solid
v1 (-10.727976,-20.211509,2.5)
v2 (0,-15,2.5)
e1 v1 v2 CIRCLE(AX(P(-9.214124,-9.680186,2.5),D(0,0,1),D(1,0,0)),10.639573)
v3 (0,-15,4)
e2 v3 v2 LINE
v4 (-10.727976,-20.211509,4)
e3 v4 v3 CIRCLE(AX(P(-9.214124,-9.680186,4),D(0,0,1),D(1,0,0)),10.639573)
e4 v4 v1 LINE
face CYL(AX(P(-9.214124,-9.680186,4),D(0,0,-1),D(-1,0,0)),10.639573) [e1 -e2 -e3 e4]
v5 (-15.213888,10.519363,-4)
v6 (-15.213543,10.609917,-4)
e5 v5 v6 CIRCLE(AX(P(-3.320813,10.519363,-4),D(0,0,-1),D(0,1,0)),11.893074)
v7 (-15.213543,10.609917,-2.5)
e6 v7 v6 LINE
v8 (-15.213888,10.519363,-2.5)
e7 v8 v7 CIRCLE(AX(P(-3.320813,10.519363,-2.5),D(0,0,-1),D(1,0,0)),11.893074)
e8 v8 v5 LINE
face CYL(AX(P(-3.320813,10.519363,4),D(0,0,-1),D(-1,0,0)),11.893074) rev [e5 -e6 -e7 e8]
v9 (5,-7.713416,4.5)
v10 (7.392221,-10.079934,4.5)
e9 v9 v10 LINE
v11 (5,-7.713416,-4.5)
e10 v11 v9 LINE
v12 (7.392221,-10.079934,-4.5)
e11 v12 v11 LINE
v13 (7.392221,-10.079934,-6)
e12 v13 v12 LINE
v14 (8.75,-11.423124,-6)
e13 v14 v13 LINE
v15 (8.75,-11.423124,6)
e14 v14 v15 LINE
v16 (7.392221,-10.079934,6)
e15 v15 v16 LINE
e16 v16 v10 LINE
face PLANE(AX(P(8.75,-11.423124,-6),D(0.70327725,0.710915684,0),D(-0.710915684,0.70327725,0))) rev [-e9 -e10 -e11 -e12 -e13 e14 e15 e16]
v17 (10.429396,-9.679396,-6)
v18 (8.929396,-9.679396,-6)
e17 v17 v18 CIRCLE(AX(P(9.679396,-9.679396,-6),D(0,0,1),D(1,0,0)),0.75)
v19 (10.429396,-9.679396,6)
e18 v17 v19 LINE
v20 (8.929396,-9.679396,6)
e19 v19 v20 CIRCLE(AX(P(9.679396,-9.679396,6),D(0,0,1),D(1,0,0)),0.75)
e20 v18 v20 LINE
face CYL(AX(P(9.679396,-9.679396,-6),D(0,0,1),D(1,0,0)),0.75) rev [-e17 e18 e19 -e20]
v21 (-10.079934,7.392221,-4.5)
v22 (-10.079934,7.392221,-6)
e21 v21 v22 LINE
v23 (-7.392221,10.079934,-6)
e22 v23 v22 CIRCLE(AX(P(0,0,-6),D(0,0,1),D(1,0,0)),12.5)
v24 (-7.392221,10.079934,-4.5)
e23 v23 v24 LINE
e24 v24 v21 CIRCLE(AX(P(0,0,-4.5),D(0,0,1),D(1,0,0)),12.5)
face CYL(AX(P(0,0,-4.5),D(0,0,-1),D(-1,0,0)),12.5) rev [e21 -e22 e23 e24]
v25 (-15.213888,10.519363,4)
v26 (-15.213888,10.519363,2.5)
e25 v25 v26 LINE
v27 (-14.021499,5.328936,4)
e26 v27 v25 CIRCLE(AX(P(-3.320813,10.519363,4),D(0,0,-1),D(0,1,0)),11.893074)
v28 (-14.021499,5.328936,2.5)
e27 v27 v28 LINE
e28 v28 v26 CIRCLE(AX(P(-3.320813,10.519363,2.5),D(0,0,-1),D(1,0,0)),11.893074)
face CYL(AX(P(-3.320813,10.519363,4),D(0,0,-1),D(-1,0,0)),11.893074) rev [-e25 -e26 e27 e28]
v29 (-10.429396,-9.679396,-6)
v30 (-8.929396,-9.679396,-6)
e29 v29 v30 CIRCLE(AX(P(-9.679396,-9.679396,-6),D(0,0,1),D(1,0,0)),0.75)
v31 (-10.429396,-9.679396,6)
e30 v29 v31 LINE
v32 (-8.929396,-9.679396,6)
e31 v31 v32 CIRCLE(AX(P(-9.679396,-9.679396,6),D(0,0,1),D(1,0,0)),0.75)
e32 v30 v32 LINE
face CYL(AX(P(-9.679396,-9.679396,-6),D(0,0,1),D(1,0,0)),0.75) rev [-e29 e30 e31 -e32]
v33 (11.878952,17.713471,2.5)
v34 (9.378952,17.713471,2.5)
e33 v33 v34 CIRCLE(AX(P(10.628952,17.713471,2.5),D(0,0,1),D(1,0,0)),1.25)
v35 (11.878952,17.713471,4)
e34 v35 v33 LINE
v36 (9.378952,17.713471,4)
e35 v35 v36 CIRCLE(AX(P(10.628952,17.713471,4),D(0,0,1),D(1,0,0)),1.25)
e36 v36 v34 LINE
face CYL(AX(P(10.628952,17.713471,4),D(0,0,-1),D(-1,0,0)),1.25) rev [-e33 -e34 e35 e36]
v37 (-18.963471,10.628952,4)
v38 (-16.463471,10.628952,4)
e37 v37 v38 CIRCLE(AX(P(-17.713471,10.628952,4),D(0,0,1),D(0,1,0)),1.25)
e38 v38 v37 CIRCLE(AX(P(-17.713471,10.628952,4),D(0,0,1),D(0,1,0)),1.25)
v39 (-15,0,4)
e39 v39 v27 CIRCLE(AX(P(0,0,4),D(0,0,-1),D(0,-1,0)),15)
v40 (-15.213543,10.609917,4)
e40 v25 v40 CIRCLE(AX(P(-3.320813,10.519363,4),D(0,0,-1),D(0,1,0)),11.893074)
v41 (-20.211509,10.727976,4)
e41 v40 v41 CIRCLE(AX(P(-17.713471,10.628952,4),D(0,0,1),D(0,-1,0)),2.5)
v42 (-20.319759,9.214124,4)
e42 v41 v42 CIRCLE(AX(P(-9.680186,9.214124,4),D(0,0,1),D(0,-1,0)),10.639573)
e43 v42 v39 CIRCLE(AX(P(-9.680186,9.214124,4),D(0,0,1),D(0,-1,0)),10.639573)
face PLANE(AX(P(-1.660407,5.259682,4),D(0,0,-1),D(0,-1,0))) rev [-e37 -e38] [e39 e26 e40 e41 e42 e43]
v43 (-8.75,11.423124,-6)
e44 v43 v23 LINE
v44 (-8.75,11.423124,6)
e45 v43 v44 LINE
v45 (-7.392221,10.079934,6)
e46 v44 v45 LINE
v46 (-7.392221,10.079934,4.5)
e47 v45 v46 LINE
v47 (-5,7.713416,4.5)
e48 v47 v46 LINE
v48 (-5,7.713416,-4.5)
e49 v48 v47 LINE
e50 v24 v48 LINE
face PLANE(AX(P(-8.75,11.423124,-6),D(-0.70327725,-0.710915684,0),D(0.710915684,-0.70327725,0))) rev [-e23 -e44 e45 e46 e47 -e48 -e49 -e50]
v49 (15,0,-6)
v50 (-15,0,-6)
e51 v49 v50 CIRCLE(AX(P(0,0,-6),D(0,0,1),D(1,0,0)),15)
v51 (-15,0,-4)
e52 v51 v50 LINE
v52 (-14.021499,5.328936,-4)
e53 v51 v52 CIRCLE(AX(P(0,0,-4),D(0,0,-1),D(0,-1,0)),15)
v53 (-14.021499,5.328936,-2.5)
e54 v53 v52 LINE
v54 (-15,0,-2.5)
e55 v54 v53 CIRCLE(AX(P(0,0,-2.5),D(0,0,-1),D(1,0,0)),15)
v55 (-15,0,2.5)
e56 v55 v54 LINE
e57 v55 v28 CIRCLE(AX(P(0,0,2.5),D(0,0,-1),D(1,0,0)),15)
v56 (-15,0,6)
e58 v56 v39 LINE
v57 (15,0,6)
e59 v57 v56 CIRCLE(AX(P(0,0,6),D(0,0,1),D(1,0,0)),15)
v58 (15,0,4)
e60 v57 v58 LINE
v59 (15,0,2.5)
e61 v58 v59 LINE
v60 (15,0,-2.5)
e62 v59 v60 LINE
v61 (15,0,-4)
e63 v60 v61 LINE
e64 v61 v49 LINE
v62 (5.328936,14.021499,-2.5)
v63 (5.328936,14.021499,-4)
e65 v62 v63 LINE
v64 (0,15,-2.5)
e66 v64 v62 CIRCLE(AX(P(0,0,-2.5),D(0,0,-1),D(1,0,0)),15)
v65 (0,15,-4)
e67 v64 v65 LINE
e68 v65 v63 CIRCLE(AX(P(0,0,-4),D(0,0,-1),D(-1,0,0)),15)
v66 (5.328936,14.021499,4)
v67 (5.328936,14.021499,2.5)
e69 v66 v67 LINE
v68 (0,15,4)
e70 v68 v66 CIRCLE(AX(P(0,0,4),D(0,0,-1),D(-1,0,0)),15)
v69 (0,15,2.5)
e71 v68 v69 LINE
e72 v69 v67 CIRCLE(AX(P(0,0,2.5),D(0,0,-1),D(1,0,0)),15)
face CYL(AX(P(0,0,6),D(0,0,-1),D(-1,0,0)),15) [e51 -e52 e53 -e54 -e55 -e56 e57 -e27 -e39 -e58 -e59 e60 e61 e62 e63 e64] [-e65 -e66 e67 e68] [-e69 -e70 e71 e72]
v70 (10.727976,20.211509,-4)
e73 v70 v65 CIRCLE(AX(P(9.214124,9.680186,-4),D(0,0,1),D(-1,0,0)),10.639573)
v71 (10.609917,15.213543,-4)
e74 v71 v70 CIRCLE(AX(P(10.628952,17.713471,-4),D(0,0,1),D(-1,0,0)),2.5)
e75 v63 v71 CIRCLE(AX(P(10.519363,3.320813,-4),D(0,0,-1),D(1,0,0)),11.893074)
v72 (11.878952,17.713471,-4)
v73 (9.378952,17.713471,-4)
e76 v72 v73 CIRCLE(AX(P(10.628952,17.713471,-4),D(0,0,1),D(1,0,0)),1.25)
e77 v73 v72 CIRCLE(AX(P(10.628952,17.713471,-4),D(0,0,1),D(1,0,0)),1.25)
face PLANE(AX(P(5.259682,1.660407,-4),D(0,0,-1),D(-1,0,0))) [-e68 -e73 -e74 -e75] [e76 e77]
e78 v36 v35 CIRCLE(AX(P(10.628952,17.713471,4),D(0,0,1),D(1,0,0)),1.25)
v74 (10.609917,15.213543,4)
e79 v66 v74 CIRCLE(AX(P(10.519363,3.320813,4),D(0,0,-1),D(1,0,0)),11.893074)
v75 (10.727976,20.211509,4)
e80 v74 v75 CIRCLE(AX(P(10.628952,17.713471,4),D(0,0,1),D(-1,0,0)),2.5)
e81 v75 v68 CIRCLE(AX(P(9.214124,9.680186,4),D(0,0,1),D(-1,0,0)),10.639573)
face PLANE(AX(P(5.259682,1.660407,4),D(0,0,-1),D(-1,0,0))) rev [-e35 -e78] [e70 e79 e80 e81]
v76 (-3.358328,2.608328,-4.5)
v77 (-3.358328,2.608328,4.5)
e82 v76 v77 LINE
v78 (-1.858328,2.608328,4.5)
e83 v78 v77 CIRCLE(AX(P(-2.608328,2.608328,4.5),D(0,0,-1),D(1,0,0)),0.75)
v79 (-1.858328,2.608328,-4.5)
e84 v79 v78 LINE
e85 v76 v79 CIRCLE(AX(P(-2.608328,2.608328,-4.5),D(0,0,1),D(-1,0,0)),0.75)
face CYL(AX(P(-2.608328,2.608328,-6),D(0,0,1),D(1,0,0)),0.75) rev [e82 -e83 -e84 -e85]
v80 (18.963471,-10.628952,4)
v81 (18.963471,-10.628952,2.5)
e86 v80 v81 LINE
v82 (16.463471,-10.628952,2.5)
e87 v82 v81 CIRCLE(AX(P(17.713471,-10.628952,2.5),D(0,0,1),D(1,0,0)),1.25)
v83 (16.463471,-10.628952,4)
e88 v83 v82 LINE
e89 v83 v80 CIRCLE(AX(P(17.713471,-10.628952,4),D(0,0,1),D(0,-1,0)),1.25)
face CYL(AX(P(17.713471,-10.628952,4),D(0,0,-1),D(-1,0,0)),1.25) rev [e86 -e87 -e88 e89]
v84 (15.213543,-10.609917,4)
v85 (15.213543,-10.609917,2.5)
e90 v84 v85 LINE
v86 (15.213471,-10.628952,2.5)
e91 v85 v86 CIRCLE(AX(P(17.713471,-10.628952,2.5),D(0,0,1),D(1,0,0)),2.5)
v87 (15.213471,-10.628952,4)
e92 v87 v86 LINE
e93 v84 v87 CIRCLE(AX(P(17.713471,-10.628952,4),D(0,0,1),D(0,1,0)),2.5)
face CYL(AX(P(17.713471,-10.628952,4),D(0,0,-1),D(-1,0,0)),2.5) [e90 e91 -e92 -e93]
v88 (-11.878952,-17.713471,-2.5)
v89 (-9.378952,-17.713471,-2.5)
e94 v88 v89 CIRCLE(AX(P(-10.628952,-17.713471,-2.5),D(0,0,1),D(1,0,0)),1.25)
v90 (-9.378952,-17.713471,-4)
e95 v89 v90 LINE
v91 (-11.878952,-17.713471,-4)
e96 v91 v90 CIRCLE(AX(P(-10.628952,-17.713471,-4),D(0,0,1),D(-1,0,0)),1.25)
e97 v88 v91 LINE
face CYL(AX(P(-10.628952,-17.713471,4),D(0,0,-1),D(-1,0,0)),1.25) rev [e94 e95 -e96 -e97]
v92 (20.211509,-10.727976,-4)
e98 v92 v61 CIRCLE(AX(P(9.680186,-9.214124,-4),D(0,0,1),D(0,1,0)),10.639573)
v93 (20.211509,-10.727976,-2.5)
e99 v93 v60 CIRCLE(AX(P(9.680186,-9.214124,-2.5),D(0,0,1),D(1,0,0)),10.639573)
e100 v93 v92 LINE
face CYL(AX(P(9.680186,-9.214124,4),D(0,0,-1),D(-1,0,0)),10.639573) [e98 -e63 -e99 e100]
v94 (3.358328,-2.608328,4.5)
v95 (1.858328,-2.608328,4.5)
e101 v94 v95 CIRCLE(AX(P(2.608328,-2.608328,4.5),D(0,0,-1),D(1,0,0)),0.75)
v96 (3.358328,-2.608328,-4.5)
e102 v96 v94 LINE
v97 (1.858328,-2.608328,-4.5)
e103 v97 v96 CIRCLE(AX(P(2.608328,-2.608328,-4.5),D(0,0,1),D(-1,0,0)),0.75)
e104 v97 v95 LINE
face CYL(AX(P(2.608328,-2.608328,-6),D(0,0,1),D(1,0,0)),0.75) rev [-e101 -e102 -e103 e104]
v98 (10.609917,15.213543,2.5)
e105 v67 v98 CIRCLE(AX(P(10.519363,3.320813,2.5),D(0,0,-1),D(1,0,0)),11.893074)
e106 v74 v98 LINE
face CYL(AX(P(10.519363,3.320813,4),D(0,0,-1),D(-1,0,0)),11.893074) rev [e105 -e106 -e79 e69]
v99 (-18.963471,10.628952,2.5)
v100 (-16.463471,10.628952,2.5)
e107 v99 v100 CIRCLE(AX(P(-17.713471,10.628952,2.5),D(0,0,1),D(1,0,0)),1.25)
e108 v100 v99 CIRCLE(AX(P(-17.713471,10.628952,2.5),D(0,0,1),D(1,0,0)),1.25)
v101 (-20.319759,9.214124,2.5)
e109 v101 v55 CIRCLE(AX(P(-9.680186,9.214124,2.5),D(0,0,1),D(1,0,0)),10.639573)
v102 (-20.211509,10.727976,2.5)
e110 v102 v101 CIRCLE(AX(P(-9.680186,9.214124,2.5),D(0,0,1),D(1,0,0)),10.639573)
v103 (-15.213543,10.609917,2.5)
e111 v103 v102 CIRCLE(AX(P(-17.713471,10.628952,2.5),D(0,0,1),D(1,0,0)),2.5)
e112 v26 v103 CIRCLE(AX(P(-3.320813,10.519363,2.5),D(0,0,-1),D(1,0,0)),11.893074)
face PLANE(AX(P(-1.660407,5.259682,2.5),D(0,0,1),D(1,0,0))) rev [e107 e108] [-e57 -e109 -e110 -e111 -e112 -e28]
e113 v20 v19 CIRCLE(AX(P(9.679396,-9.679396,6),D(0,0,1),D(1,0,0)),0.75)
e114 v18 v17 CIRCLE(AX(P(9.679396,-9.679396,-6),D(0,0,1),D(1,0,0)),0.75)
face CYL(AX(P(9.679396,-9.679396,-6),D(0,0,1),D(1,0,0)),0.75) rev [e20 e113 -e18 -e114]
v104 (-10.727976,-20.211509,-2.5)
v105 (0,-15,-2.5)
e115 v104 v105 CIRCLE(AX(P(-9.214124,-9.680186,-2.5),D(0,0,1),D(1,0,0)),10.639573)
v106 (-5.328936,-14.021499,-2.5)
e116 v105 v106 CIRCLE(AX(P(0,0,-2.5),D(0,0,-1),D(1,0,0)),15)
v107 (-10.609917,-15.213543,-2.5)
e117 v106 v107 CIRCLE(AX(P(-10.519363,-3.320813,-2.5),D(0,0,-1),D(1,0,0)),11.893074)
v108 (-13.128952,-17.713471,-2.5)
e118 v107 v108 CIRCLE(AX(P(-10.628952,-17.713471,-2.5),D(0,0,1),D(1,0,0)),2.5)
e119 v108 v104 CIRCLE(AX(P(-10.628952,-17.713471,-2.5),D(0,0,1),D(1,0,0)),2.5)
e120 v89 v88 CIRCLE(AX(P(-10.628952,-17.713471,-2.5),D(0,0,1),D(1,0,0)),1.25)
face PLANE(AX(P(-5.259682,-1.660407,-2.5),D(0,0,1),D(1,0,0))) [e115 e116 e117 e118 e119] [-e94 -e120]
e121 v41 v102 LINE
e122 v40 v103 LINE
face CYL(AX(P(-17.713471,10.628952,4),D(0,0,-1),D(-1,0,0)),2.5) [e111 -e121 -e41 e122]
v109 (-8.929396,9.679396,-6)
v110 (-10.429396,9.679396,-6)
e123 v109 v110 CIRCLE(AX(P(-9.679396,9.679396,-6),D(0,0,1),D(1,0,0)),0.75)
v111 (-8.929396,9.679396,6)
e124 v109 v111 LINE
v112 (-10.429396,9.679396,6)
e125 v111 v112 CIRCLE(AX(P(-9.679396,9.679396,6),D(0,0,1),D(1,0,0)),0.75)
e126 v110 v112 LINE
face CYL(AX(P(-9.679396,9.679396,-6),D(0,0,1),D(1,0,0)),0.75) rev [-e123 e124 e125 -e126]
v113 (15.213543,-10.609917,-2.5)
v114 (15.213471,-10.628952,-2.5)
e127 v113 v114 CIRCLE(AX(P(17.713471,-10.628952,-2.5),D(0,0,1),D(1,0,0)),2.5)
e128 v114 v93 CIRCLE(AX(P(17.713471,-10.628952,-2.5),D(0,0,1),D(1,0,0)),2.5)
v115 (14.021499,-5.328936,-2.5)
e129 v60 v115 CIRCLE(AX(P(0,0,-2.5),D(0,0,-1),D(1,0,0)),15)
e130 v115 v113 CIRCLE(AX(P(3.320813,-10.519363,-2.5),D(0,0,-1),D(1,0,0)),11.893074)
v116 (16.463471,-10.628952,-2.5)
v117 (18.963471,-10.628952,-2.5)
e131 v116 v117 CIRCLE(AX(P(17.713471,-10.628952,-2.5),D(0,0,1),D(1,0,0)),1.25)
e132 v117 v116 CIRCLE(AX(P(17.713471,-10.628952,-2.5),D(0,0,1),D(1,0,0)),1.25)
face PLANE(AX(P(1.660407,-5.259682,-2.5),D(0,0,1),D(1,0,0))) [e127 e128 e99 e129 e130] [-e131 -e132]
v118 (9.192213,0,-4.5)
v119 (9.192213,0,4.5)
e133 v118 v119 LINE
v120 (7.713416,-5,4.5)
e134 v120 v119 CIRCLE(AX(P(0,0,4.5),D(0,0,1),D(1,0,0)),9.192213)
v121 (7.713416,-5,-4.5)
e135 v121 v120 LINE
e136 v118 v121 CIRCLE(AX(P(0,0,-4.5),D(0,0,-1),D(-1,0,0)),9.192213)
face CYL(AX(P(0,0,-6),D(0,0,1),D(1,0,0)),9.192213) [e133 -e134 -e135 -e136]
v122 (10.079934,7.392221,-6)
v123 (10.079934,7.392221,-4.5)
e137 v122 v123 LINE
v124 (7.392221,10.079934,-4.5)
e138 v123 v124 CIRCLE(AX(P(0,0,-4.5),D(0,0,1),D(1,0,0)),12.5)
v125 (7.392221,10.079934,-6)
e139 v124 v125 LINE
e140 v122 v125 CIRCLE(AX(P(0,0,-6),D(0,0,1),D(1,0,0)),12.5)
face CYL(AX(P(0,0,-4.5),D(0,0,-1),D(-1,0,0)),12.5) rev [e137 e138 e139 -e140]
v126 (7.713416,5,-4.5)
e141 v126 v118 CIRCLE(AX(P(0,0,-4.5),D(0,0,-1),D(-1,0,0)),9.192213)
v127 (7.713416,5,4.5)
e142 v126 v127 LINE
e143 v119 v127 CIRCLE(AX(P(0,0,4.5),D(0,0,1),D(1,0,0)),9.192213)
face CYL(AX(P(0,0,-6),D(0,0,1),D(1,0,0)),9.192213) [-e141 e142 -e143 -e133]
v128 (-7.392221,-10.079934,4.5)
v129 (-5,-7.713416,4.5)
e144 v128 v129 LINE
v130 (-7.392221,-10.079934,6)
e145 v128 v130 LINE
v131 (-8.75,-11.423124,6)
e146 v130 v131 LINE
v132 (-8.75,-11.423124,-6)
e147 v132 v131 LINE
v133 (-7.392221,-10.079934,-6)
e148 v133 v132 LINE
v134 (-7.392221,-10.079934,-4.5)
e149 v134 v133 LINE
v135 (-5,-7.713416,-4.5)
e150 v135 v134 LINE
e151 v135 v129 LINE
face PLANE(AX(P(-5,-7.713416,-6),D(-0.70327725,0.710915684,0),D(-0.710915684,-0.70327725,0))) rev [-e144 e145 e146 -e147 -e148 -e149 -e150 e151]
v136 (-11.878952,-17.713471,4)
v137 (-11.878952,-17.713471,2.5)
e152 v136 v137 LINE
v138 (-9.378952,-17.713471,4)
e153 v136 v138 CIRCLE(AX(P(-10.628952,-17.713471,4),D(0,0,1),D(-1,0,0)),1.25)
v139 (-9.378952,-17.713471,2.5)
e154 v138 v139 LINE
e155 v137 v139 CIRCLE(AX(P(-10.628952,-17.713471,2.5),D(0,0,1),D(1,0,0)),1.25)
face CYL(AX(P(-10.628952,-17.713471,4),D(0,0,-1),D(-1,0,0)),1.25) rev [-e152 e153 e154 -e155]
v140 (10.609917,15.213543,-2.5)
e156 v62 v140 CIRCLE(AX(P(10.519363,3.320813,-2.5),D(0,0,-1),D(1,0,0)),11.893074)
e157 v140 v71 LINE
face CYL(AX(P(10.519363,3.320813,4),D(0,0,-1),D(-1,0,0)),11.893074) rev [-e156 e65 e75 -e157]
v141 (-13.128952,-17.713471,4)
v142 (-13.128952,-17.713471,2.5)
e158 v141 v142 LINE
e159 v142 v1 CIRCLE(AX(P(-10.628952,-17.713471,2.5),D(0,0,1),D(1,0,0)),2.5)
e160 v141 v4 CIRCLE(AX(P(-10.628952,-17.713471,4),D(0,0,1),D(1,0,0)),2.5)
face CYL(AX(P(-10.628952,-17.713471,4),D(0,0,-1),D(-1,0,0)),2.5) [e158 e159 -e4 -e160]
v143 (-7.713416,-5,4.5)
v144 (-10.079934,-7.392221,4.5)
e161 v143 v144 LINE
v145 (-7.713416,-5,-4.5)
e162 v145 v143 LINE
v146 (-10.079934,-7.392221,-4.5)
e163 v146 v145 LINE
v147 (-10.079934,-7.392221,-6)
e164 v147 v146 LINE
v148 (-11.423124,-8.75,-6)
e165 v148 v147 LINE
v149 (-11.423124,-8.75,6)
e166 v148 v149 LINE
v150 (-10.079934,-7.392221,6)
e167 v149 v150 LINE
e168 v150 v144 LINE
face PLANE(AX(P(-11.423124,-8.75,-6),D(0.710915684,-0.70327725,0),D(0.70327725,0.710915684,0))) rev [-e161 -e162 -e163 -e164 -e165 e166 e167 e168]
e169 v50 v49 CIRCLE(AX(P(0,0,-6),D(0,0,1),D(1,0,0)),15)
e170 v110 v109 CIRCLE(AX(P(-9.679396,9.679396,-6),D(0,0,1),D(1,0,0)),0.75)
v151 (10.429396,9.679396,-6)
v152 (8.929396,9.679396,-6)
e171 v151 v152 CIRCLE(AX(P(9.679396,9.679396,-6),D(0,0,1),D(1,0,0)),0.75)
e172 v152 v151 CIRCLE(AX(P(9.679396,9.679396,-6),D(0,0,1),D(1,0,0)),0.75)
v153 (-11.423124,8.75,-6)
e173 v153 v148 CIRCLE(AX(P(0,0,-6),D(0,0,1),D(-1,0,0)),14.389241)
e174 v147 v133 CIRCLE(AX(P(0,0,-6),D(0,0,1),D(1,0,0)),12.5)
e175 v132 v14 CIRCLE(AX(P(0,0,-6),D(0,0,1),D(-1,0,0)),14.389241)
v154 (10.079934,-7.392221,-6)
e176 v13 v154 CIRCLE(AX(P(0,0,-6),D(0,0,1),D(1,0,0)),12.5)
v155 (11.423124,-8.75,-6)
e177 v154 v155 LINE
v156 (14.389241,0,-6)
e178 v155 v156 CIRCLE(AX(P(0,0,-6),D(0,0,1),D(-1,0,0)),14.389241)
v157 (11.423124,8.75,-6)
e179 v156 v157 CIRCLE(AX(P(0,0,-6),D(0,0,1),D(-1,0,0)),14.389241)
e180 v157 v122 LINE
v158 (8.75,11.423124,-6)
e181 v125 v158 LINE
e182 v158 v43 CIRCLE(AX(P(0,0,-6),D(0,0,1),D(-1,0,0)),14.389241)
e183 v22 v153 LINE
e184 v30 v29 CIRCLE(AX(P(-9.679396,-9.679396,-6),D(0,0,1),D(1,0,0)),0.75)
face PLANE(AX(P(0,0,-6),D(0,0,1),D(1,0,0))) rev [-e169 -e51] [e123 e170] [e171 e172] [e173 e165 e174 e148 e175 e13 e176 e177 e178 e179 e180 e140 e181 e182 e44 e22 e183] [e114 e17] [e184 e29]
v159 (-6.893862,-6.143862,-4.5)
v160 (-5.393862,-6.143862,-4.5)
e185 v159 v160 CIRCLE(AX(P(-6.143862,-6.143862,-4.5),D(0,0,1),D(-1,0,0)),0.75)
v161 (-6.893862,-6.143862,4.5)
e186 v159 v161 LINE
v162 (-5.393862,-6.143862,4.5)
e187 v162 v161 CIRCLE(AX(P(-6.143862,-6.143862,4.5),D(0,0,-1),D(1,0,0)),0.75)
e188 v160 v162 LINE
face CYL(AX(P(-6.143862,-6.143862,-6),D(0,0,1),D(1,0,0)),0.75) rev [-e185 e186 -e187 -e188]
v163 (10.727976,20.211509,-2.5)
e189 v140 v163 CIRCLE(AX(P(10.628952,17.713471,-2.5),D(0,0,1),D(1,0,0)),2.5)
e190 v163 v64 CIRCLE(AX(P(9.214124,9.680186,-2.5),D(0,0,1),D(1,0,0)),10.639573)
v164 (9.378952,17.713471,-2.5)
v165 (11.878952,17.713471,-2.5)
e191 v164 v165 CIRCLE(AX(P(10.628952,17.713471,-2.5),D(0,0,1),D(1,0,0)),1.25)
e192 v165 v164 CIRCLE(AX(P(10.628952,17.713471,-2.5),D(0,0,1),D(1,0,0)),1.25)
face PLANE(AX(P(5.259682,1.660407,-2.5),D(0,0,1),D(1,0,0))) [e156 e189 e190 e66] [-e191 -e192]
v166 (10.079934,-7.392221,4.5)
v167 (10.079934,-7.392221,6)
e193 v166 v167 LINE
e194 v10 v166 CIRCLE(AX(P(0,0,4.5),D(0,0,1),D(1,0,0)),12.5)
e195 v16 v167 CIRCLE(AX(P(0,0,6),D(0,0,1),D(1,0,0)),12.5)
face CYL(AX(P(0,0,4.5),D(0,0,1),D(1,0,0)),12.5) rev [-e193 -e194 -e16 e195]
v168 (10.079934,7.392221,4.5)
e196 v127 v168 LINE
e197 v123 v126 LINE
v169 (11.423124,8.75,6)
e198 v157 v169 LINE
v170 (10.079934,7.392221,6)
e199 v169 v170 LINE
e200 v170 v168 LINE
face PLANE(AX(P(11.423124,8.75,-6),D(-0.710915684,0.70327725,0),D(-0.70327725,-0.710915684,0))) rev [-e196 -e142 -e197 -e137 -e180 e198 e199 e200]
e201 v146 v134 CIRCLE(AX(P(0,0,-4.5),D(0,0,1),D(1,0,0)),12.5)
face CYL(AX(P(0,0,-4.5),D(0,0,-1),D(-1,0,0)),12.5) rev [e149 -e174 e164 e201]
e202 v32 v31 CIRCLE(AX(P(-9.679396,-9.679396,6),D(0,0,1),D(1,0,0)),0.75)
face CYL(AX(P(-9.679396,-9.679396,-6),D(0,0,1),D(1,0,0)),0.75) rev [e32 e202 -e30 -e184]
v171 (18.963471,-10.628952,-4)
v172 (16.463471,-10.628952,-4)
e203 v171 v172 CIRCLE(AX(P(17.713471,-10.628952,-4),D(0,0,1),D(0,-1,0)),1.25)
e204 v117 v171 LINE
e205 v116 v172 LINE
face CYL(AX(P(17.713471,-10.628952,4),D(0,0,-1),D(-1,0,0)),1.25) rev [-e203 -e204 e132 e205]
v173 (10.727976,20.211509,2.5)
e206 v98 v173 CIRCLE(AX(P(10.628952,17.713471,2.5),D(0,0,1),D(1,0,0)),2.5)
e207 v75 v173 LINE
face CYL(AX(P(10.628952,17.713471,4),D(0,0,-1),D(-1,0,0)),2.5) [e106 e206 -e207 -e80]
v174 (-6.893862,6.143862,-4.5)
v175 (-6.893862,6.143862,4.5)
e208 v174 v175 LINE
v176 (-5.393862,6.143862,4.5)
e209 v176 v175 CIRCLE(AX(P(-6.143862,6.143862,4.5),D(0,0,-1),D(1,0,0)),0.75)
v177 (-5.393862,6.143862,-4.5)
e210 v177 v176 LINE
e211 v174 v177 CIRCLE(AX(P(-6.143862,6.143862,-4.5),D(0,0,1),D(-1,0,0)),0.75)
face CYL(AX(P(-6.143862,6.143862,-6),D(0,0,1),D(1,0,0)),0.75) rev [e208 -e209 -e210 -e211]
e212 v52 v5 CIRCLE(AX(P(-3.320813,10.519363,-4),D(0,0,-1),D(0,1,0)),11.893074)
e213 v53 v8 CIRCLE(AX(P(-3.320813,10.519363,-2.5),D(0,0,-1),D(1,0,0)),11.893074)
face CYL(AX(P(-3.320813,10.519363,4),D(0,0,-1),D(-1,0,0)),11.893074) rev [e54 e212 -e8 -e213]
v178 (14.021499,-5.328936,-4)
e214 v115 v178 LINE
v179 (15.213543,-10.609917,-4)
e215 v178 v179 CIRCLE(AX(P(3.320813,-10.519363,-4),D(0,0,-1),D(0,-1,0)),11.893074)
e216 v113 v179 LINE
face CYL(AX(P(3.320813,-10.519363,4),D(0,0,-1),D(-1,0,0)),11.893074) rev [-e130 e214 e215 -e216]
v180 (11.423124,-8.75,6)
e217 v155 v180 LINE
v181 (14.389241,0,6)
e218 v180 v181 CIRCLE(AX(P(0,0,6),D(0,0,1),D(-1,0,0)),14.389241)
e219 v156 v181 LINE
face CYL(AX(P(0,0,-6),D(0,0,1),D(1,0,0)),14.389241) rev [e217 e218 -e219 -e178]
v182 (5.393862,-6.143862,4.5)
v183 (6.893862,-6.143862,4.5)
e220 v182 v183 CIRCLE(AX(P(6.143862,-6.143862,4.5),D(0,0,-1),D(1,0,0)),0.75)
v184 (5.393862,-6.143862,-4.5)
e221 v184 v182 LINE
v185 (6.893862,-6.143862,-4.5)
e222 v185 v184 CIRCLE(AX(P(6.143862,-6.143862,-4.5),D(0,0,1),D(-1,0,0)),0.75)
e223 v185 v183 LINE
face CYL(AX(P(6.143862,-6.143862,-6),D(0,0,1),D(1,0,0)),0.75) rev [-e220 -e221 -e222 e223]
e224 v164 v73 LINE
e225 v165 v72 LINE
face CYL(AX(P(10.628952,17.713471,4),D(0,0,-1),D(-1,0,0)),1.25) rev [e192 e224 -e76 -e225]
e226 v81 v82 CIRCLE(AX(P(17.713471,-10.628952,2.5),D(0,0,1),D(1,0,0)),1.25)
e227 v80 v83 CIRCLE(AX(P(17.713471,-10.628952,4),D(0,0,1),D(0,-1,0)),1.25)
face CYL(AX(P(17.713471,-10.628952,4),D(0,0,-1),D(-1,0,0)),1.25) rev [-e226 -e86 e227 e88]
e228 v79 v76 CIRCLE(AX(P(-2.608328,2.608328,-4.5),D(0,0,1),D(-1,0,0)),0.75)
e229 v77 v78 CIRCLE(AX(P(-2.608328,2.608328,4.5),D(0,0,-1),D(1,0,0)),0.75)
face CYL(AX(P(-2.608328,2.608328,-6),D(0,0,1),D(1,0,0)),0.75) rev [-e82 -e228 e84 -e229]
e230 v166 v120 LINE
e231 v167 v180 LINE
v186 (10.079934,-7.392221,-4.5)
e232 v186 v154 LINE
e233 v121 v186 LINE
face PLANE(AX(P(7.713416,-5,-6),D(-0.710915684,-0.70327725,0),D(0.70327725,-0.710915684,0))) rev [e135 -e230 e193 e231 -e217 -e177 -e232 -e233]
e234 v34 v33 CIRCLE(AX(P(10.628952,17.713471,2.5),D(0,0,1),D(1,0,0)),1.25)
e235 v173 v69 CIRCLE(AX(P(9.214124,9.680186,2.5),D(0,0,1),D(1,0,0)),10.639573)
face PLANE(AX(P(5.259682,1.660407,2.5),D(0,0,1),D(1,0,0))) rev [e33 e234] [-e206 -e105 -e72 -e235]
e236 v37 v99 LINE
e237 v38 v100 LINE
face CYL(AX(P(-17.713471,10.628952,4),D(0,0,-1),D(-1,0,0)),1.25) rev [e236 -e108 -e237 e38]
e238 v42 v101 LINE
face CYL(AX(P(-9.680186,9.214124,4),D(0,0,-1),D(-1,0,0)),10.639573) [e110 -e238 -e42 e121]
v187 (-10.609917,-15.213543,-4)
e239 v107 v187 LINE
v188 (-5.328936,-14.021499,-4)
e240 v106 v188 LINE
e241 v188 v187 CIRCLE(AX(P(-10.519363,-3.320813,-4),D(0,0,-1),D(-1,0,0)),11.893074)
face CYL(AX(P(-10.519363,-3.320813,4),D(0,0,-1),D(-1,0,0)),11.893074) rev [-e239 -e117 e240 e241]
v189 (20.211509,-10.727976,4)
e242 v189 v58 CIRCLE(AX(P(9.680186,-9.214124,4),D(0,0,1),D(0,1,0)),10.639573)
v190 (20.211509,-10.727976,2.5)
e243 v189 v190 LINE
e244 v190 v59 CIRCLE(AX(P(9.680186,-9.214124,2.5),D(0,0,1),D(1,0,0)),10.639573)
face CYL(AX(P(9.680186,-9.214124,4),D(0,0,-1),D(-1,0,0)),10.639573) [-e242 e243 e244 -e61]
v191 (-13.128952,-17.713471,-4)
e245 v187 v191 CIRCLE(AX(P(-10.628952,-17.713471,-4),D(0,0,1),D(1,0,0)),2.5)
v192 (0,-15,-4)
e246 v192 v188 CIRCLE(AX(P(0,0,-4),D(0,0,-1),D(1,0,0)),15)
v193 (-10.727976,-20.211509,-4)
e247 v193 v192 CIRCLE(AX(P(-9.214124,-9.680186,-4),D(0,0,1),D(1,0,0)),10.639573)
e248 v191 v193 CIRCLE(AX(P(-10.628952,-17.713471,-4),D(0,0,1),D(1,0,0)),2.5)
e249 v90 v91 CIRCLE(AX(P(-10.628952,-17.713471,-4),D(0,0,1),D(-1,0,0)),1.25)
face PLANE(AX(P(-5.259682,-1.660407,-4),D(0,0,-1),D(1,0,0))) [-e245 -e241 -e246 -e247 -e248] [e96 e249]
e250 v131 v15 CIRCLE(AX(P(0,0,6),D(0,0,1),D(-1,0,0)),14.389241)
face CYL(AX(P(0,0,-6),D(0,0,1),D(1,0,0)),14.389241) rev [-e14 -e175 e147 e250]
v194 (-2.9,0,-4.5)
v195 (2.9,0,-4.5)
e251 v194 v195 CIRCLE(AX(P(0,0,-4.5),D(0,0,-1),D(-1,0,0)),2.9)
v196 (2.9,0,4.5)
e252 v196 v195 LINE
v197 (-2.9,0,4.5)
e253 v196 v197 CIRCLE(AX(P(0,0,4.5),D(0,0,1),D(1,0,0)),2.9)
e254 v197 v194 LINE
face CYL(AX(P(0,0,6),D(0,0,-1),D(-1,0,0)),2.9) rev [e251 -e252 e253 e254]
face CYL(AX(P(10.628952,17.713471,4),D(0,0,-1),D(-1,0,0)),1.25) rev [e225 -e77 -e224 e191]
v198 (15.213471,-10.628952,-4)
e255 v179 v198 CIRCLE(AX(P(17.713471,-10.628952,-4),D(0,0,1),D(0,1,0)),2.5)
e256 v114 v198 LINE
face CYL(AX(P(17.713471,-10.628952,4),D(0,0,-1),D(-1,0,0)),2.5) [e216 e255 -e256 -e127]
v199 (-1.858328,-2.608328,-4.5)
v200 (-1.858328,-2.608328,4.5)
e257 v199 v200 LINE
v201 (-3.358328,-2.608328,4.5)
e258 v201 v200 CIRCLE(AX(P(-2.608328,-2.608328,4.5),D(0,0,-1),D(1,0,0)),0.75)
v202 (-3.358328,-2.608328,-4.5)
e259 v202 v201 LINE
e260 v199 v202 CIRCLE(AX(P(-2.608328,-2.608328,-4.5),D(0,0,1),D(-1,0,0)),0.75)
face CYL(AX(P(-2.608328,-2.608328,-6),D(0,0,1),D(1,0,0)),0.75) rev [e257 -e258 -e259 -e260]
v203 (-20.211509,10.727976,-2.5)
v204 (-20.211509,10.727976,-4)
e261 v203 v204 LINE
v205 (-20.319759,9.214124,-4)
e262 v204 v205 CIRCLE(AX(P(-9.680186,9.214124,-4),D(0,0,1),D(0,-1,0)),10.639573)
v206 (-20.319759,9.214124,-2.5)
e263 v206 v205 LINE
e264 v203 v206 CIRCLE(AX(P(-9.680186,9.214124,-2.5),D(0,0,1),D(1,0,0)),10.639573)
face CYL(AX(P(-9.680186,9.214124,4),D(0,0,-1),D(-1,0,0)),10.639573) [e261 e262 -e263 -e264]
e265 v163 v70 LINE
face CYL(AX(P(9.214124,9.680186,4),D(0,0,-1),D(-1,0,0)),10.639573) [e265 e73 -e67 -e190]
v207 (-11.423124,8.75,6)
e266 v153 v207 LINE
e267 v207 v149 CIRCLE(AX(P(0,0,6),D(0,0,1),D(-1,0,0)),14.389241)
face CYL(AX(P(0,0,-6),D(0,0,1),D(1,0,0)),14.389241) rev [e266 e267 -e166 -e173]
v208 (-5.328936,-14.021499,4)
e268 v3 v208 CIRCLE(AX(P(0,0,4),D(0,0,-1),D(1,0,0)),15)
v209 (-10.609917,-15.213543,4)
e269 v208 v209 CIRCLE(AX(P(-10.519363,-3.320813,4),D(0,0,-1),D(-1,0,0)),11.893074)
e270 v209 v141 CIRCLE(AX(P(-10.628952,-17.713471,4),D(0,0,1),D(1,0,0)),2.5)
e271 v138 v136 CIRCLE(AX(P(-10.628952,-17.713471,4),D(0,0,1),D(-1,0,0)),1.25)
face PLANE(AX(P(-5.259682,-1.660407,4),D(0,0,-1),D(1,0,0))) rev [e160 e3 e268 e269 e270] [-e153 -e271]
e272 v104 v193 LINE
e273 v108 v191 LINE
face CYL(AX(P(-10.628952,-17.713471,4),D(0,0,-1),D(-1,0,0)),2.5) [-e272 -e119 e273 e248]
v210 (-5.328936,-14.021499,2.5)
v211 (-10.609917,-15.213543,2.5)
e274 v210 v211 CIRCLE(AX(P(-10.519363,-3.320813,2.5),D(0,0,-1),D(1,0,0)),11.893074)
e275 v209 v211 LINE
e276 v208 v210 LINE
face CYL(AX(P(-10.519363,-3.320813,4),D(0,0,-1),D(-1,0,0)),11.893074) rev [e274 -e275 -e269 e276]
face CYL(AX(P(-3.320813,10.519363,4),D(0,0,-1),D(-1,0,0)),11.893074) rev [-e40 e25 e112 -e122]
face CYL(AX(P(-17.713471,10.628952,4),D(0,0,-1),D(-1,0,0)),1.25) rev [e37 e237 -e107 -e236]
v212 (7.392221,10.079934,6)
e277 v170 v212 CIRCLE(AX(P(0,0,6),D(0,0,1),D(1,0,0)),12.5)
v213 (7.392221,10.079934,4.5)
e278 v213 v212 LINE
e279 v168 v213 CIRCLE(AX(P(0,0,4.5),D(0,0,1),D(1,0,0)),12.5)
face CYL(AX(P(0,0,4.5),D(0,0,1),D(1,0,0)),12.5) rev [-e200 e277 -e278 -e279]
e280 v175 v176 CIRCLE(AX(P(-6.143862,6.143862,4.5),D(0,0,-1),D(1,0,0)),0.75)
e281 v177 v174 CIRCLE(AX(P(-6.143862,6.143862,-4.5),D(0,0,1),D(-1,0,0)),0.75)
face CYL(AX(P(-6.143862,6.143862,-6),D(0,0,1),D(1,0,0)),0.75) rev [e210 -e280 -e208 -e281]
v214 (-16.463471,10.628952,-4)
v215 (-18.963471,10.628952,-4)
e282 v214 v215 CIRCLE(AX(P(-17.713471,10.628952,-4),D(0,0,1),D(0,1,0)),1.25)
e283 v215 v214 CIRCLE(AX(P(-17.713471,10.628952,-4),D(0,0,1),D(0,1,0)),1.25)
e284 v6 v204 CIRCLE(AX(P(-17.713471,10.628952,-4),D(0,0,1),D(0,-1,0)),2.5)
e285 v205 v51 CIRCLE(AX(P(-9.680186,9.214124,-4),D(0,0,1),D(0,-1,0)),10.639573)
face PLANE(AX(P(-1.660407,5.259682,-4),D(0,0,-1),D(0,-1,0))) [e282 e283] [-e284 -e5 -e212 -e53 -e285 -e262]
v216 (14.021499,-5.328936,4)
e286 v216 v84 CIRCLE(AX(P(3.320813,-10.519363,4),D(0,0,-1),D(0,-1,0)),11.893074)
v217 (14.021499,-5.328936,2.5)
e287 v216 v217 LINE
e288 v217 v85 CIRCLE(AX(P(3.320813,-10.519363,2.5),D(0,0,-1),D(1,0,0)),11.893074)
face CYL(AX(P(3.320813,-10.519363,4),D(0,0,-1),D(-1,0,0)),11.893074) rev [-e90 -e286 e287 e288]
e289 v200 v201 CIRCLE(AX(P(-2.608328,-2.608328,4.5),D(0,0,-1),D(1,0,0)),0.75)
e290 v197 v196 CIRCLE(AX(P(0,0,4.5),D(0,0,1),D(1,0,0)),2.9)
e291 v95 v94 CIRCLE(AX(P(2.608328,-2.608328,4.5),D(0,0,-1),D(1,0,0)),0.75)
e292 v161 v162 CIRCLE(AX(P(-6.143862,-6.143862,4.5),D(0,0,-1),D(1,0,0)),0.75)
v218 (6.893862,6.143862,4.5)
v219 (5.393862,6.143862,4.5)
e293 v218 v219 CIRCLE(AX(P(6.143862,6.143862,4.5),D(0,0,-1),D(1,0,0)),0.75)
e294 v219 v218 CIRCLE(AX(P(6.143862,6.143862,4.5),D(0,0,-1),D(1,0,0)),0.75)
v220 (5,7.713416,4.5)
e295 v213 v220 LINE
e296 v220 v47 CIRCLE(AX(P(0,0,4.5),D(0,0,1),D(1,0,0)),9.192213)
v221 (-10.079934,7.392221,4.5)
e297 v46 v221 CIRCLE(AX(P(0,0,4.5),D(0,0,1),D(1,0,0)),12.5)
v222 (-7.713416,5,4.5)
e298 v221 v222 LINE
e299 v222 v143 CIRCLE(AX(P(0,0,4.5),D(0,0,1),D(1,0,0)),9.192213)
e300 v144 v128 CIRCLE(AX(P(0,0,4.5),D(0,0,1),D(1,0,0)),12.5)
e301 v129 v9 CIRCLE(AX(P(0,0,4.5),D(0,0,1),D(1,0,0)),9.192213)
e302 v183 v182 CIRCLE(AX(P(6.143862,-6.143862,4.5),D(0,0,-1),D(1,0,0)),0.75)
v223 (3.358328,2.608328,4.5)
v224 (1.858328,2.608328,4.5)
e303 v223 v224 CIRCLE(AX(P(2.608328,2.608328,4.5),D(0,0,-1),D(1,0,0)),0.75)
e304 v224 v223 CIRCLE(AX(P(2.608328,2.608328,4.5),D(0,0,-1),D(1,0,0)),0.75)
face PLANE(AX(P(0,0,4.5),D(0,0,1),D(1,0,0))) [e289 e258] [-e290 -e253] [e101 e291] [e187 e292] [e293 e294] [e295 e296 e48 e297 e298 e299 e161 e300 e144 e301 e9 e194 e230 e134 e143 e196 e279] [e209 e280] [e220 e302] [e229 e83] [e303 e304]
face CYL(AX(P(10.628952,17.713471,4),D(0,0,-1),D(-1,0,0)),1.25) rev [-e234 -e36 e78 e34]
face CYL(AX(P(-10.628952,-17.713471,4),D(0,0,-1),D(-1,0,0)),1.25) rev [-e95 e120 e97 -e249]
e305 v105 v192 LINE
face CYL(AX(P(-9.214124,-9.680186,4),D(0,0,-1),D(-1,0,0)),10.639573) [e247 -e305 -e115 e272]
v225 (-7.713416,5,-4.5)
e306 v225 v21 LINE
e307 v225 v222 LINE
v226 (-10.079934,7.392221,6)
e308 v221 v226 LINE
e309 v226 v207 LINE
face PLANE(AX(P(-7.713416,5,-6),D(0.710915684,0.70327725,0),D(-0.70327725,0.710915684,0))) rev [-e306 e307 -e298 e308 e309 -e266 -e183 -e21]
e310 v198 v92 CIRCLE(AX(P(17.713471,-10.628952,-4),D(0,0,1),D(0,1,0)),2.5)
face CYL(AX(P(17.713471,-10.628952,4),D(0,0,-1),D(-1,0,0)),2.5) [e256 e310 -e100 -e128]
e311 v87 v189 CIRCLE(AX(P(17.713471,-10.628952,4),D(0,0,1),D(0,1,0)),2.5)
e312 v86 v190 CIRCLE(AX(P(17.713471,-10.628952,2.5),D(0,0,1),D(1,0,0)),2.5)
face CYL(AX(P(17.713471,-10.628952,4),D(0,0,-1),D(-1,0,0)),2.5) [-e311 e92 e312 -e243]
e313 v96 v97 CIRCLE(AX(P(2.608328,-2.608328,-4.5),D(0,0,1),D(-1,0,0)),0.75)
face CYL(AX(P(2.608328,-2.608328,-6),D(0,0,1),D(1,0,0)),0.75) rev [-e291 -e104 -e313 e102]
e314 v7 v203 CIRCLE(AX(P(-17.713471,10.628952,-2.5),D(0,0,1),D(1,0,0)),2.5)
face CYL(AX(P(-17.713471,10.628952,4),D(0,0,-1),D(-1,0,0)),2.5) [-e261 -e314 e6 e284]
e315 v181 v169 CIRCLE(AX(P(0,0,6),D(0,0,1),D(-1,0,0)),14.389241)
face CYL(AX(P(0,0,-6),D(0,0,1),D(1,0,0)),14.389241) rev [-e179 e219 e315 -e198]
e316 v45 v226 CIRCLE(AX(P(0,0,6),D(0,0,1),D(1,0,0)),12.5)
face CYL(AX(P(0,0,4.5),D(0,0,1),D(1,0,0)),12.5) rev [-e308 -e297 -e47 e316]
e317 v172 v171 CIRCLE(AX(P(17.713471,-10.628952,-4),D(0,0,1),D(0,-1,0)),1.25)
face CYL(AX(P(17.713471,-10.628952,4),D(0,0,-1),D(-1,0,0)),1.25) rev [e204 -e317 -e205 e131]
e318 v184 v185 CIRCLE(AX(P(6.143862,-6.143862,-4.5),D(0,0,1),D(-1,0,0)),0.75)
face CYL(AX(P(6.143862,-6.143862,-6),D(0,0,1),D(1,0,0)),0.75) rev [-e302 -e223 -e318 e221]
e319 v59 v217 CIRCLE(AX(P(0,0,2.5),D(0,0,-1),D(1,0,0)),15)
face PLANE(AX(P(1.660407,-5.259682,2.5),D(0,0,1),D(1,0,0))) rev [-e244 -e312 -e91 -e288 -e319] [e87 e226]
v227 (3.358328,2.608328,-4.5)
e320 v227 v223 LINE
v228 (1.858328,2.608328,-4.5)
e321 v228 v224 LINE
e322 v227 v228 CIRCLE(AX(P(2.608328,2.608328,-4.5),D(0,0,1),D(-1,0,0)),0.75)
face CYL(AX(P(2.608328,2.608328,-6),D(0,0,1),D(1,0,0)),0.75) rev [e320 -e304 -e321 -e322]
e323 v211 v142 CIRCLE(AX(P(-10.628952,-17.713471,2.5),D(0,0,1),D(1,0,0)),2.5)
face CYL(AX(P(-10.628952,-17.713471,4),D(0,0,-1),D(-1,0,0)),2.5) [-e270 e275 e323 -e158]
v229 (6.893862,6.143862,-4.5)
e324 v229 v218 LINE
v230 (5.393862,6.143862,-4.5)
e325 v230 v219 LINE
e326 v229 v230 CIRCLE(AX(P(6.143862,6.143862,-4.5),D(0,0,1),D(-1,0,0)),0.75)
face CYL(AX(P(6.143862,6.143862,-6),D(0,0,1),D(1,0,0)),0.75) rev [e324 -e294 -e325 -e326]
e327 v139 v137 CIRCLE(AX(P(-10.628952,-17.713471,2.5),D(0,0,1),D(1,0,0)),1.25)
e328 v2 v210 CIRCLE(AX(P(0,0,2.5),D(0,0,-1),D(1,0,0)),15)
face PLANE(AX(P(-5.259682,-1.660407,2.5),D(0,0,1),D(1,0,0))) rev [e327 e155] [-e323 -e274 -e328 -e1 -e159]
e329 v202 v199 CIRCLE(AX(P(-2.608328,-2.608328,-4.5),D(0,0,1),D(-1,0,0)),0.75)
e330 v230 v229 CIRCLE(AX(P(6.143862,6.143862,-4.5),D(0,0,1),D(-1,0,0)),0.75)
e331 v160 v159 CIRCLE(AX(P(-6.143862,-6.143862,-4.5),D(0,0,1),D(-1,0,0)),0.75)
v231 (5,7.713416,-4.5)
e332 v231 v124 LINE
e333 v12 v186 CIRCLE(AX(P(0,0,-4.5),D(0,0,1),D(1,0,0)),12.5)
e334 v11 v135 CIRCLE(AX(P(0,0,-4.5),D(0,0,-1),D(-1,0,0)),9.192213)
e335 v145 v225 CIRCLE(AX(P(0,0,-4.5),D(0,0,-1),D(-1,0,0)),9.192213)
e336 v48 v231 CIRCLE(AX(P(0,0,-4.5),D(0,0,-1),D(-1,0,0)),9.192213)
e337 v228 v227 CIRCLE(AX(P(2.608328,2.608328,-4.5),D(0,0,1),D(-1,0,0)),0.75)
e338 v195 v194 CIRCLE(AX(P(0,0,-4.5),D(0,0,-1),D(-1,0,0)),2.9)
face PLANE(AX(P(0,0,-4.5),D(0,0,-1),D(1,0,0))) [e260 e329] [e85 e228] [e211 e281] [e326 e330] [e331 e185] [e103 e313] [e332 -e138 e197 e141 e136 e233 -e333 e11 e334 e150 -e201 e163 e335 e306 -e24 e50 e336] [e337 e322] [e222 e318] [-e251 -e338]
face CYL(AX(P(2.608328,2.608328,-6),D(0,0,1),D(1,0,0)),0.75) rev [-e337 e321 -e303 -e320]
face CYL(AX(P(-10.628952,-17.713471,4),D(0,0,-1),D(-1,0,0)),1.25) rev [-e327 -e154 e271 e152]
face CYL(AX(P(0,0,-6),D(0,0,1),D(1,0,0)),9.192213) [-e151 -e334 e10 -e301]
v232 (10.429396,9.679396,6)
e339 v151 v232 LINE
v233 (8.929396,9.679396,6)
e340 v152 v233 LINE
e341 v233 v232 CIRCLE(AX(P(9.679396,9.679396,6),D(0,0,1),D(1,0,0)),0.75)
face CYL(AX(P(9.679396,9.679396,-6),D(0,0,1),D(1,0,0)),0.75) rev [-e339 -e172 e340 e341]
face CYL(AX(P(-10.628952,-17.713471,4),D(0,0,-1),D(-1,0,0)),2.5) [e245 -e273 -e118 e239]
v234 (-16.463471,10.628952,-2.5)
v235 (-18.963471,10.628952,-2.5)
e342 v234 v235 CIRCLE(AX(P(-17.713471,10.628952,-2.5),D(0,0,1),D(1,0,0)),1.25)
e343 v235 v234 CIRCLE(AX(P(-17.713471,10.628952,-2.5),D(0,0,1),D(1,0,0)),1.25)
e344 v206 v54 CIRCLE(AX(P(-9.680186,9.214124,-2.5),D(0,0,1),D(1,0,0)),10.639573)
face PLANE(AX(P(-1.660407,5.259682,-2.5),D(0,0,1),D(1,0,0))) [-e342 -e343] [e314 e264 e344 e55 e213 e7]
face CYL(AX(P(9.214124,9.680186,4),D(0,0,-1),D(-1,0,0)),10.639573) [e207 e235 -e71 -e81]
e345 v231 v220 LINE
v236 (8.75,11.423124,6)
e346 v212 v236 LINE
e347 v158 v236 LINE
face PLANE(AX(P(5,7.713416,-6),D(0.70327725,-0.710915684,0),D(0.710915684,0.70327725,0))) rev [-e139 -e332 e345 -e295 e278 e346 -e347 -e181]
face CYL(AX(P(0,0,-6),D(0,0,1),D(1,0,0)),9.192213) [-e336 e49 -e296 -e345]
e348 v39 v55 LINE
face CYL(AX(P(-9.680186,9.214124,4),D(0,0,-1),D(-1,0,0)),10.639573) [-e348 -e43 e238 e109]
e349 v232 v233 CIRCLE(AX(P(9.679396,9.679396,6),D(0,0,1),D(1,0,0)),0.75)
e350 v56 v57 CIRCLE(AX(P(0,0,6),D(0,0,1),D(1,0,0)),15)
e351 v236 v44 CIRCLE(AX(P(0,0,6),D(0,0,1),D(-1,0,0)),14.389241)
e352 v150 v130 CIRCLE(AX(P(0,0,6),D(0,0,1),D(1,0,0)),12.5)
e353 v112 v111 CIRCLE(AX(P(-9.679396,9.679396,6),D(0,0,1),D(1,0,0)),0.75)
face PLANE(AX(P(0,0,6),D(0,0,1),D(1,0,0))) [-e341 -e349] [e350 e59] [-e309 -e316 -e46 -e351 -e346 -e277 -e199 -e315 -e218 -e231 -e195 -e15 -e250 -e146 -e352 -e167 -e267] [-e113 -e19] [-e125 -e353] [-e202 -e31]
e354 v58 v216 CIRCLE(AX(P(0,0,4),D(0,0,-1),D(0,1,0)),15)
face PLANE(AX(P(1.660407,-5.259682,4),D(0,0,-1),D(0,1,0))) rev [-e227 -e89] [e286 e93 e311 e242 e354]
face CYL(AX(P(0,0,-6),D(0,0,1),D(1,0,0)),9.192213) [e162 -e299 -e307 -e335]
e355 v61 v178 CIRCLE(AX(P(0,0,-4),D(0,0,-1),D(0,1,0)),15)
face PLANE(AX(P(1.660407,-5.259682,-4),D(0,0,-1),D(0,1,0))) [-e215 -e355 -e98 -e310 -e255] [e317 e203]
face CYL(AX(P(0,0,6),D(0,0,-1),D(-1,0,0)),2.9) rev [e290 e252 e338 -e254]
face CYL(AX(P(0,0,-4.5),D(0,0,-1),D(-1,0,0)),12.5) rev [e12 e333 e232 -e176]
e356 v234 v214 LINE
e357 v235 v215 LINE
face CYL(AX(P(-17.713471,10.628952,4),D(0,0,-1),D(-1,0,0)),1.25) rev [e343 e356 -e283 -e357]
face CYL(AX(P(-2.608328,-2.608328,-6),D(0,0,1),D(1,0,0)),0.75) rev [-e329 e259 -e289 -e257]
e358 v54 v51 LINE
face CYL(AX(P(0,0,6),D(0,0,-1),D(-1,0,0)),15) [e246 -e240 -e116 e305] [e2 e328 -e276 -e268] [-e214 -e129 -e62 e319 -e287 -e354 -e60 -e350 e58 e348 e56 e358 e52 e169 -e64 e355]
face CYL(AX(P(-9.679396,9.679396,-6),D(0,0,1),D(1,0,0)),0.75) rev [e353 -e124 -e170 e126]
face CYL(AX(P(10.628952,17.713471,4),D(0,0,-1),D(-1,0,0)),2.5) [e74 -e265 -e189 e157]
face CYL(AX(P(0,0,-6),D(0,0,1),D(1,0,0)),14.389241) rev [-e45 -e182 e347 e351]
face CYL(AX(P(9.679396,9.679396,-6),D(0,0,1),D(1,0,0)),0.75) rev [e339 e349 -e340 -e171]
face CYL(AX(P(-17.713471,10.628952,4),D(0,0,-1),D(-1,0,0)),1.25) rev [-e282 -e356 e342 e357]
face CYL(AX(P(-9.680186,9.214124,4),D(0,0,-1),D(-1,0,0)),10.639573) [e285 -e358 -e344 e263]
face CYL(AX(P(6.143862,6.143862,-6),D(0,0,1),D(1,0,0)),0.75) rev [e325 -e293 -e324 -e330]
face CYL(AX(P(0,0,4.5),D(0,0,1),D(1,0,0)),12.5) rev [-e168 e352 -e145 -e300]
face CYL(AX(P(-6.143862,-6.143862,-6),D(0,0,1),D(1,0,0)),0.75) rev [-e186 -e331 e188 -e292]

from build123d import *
from build123d.topology import SkipClean

# Parameters (mm, degrees)
SKETCH1_R           = 30
SKETCH1_R_2         = 5.8
BOSS_EXTRUDE1_DEPTH = 12
CUT_EXTRUDE1_DEPTH  = 49.744230428
SKETCH3_R           = 1.5
CUT_EXTRUDE2_DEPTH  = 49.744230428
SKETCH4_R           = 25
CUT_EXTRUDE3_DEPTH  = 3
SKETCH5_R           = 2.5
BOSS_EXTRUDE2_DEPTH = 8
CIRPATTERN1_COUNT   = 4
CUT_EXTRUDE11_DEPTH = 2.5
SCALE_1_SCALE       = 0.5
CUT_EXTRUDE12_DEPTH = 2.5


with BuildPart() as part:
    # Sketch1 → Boss-Extrude1 (new, symmetric)
    with BuildSketch(Plane.XY):
        Circle(SKETCH1_R)
        Circle(SKETCH1_R_2, mode=Mode.SUBTRACT)
    extrude(amount=BOSS_EXTRUDE1_DEPTH, both=True)

    # Sketch2 → Cut-Extrude1 (cut, through all)
    with BuildSketch(Plane.XY.offset(12)):
        with BuildLine():
            Line((-17.5, 22.846247275), (-10, 15.426831039))
            ThreePointArc((-10, 15.426831039), (0, 18.384425906), (10, 15.426831039))
            Line((10, 15.426831039), (17.5, 22.846247275))
            ThreePointArc((17.5, 22.846247275), (0, 28.778481797), (-17.5, 22.846247275))
        make_face()
        with BuildLine():
            Line((15.426831039, -10), (22.846247275, -17.5))
            ThreePointArc((22.846247275, -17.5), (28.778481797, 0), (22.846247275, 17.5))
            Line((22.846247275, 17.5), (15.426831039, 10))
            ThreePointArc((15.426831039, 10), (18.384425906, 0), (15.426831039, -10))
        make_face()
        with BuildLine():
            Line((-10, -15.426831039), (-17.5, -22.846247275))
            ThreePointArc((-17.5, -22.846247275), (0, -28.778481797), (17.5, -22.846247275))
            Line((17.5, -22.846247275), (10, -15.426831039))
            ThreePointArc((10, -15.426831039), (0, -18.384425906), (-10, -15.426831039))
        make_face()
        with BuildLine():
            Line((-15.426831039, 10), (-22.846247275, 17.5))
            ThreePointArc((-22.846247275, 17.5), (-28.778481797, 0), (-22.846247275, -17.5))
            Line((-22.846247275, -17.5), (-15.426831039, -10))
            ThreePointArc((-15.426831039, -10), (-18.384425906, 0), (-15.426831039, 10))
        make_face()
    extrude(amount=-CUT_EXTRUDE1_DEPTH, mode=Mode.SUBTRACT)

    # Sketch3 → Cut-Extrude2 (cut, through all)
    with BuildSketch(Plane.XY.offset(12)):
        with Locations((-19.358791633, 19.358791633)):
            Circle(SKETCH3_R)
        with Locations((-12.287723821, 12.287723821)):
            Circle(SKETCH3_R)
        with Locations((-5.216656009, 5.216656009)):
            Circle(SKETCH3_R)
        with Locations((19.358791633, 19.358791633)):
            Circle(SKETCH3_R)
        with Locations((12.287723821, 12.287723821)):
            Circle(SKETCH3_R)
        with Locations((5.216656009, 5.216656009)):
            Circle(SKETCH3_R)
        with Locations((19.358791633, -19.358791633)):
            Circle(SKETCH3_R)
        with Locations((12.287723821, -12.287723821)):
            Circle(SKETCH3_R)
        with Locations((5.216656009, -5.216656009)):
            Circle(SKETCH3_R)
        with Locations((-19.358791633, -19.358791633)):
            Circle(SKETCH3_R)
        with Locations((-12.287723821, -12.287723821)):
            Circle(SKETCH3_R)
        with Locations((-5.216656009, -5.216656009)):
            Circle(SKETCH3_R)
    extrude(amount=-CUT_EXTRUDE2_DEPTH, mode=Mode.SUBTRACT)

    # Sketch4 → Cut-Extrude3 (cut)
    with BuildSketch(Plane.XY.offset(12)):
        Circle(SKETCH4_R)
    cut_extrude3 = extrude(amount=-CUT_EXTRUDE3_DEPTH, mode=Mode.SUBTRACT)

    # Mirror1: Cut-Extrude3 across plane
    add(cut_extrude3.mirror(Plane.XY), mode=Mode.SUBTRACT)

    # Sketch5 → Boss-Extrude2 (add, symmetric)
    with BuildSketch(Plane.XY):
        with BuildLine():
            ThreePointArc((0, 30), (9.130183529, 38.500591706), (21.455952915, 40.423017172))
            ThreePointArc((21.455952915, 40.423017172), (26.256509779, 35.30886651), (21.219834085, 30.427085978))
            ThreePointArc((21.219834085, 30.427085978), (15.801391202, 29.844023046), (10.657871278, 28.042998767))
            ThreePointArc((10.657871278, 28.042998767), (5.418027178, 29.506693842), (0, 30))
        make_face()
        with Locations((21.257904133, 35.426941044)):
            Circle(SKETCH5_R, mode=Mode.SUBTRACT)
    boss_extrude2 = extrude(amount=BOSS_EXTRUDE2_DEPTH, both=True)

    # CirPattern1: Boss-Extrude2 ×4 about axis
    cirpattern1_axis = Axis((0, 0, 0), (0, 0, 1))
    for i in range(1, CIRPATTERN1_COUNT):
        add(boss_extrude2.rotate(cirpattern1_axis, i * 360 / CIRPATTERN1_COUNT))

    # Sketch16 → Cut-Extrude11 (cut, symmetric)
    with SkipClean():  # the faces are left unmerged after this step: merging them gives an invalid solid
        with BuildSketch(Plane.XY):
            with BuildLine():
                ThreePointArc((-10.657871278, -28.042998767), (-5.418027178, -29.506693842), (0, -30))
                ThreePointArc((0, -30), (-9.130183529, -38.500591706), (-21.455952915, -40.423017172))
                ThreePointArc((-21.455952915, -40.423017172), (-26.256509779, -35.30886651), (-21.219834085, -30.427085978))
                ThreePointArc((-21.219834085, -30.427085978), (-15.801391202, -29.844023046), (-10.657871278, -28.042998767))
            make_face()
            with BuildLine():
                ThreePointArc((28.042998767, -10.657871278), (29.506693842, -5.418027178), (30, 0))
                ThreePointArc((30, 0), (38.500591706, -9.130183529), (40.423017172, -21.455952915))
                ThreePointArc((40.423017172, -21.455952915), (35.30886651, -26.256509779), (30.427085978, -21.219834085))
                ThreePointArc((30.427085978, -21.219834085), (29.844023046, -15.801391202), (28.042998767, -10.657871278))
            make_face()
            with BuildLine():
                ThreePointArc((10.657871278, 28.042998767), (5.418027178, 29.506693842), (0, 30))
                ThreePointArc((0, 30), (9.130183529, 38.500591706), (21.455952915, 40.423017172))
                ThreePointArc((21.455952915, 40.423017172), (26.256509779, 35.30886651), (21.219834085, 30.427085978))
                ThreePointArc((21.219834085, 30.427085978), (15.801391202, 29.844023046), (10.657871278, 28.042998767))
            make_face()
            with BuildLine():
                ThreePointArc((-28.042998767, 10.657871278), (-29.506693842, 5.418027178), (-30, 0))
                ThreePointArc((-30, 0), (-38.500591706, 9.130183529), (-40.423017172, 21.455952915))
                ThreePointArc((-40.423017172, 21.455952915), (-35.30886651, 26.256509779), (-30.427085978, 21.219834085))
                ThreePointArc((-30.427085978, 21.219834085), (-29.844023046, 15.801391202), (-28.042998767, 10.657871278))
            make_face()
        extrude(amount=CUT_EXTRUDE11_DEPTH, both=True, mode=Mode.SUBTRACT)


with BuildPart() as part_1:
    # Scale 1: scaled about (0, 0, 0)
    add(part.part.scale(SCALE_1_SCALE))

    # Sketch17 → Cut-Extrude12 (cut, symmetric)
    with SkipClean():  # the faces are left unmerged after this step: merging them gives an invalid solid
        with BuildSketch(Plane.XY):
            with BuildLine():
                ThreePointArc((-5.328935639, -14.021499383), (-2.709013589, -14.753346921), (0, -15))
                ThreePointArc((0, -15), (-4.565091764, -19.250295853), (-10.727976457, -20.211508586))
                ThreePointArc((-10.727976457, -20.211508586), (-13.128254889, -17.654433255), (-10.609917043, -15.213542989))
                ThreePointArc((-10.609917043, -15.213542989), (-7.900695601, -14.922011523), (-5.328935639, -14.021499383))
            make_face()
            with BuildLine():
                ThreePointArc((14.021499383, -5.328935639), (14.753346921, -2.709013589), (15, 0))
                ThreePointArc((15, 0), (19.250295853, -4.565091764), (20.211508586, -10.727976457))
                ThreePointArc((20.211508586, -10.727976457), (17.654433255, -13.128254889), (15.213542989, -10.609917043))
                ThreePointArc((15.213542989, -10.609917043), (14.922011523, -7.900695601), (14.021499383, -5.328935639))
            make_face()
            with BuildLine():
                ThreePointArc((5.328935639, 14.021499383), (2.709013589, 14.753346921), (0, 15))
                ThreePointArc((0, 15), (4.565091764, 19.250295853), (10.727976457, 20.211508586))
                ThreePointArc((10.727976457, 20.211508586), (13.128254889, 17.654433255), (10.609917043, 15.213542989))
                ThreePointArc((10.609917043, 15.213542989), (7.900695601, 14.922011523), (5.328935639, 14.021499383))
            make_face()
            with BuildLine():
                ThreePointArc((-14.021499383, 5.328935639), (-14.753346921, 2.709013589), (-15, 0))
                ThreePointArc((-15, 0), (-19.250295853, 4.565091764), (-20.211508586, 10.727976457))
                ThreePointArc((-20.211508586, 10.727976457), (-17.654433255, 13.128254889), (-15.213542989, 10.609917043))
                ThreePointArc((-15.213542989, 10.609917043), (-14.922011523, 7.900695601), (-14.021499383, 5.328935639))
            make_face()
        extrude(amount=CUT_EXTRUDE12_DEPTH, both=True, mode=Mode.SUBTRACT)


solid = part_1.part
